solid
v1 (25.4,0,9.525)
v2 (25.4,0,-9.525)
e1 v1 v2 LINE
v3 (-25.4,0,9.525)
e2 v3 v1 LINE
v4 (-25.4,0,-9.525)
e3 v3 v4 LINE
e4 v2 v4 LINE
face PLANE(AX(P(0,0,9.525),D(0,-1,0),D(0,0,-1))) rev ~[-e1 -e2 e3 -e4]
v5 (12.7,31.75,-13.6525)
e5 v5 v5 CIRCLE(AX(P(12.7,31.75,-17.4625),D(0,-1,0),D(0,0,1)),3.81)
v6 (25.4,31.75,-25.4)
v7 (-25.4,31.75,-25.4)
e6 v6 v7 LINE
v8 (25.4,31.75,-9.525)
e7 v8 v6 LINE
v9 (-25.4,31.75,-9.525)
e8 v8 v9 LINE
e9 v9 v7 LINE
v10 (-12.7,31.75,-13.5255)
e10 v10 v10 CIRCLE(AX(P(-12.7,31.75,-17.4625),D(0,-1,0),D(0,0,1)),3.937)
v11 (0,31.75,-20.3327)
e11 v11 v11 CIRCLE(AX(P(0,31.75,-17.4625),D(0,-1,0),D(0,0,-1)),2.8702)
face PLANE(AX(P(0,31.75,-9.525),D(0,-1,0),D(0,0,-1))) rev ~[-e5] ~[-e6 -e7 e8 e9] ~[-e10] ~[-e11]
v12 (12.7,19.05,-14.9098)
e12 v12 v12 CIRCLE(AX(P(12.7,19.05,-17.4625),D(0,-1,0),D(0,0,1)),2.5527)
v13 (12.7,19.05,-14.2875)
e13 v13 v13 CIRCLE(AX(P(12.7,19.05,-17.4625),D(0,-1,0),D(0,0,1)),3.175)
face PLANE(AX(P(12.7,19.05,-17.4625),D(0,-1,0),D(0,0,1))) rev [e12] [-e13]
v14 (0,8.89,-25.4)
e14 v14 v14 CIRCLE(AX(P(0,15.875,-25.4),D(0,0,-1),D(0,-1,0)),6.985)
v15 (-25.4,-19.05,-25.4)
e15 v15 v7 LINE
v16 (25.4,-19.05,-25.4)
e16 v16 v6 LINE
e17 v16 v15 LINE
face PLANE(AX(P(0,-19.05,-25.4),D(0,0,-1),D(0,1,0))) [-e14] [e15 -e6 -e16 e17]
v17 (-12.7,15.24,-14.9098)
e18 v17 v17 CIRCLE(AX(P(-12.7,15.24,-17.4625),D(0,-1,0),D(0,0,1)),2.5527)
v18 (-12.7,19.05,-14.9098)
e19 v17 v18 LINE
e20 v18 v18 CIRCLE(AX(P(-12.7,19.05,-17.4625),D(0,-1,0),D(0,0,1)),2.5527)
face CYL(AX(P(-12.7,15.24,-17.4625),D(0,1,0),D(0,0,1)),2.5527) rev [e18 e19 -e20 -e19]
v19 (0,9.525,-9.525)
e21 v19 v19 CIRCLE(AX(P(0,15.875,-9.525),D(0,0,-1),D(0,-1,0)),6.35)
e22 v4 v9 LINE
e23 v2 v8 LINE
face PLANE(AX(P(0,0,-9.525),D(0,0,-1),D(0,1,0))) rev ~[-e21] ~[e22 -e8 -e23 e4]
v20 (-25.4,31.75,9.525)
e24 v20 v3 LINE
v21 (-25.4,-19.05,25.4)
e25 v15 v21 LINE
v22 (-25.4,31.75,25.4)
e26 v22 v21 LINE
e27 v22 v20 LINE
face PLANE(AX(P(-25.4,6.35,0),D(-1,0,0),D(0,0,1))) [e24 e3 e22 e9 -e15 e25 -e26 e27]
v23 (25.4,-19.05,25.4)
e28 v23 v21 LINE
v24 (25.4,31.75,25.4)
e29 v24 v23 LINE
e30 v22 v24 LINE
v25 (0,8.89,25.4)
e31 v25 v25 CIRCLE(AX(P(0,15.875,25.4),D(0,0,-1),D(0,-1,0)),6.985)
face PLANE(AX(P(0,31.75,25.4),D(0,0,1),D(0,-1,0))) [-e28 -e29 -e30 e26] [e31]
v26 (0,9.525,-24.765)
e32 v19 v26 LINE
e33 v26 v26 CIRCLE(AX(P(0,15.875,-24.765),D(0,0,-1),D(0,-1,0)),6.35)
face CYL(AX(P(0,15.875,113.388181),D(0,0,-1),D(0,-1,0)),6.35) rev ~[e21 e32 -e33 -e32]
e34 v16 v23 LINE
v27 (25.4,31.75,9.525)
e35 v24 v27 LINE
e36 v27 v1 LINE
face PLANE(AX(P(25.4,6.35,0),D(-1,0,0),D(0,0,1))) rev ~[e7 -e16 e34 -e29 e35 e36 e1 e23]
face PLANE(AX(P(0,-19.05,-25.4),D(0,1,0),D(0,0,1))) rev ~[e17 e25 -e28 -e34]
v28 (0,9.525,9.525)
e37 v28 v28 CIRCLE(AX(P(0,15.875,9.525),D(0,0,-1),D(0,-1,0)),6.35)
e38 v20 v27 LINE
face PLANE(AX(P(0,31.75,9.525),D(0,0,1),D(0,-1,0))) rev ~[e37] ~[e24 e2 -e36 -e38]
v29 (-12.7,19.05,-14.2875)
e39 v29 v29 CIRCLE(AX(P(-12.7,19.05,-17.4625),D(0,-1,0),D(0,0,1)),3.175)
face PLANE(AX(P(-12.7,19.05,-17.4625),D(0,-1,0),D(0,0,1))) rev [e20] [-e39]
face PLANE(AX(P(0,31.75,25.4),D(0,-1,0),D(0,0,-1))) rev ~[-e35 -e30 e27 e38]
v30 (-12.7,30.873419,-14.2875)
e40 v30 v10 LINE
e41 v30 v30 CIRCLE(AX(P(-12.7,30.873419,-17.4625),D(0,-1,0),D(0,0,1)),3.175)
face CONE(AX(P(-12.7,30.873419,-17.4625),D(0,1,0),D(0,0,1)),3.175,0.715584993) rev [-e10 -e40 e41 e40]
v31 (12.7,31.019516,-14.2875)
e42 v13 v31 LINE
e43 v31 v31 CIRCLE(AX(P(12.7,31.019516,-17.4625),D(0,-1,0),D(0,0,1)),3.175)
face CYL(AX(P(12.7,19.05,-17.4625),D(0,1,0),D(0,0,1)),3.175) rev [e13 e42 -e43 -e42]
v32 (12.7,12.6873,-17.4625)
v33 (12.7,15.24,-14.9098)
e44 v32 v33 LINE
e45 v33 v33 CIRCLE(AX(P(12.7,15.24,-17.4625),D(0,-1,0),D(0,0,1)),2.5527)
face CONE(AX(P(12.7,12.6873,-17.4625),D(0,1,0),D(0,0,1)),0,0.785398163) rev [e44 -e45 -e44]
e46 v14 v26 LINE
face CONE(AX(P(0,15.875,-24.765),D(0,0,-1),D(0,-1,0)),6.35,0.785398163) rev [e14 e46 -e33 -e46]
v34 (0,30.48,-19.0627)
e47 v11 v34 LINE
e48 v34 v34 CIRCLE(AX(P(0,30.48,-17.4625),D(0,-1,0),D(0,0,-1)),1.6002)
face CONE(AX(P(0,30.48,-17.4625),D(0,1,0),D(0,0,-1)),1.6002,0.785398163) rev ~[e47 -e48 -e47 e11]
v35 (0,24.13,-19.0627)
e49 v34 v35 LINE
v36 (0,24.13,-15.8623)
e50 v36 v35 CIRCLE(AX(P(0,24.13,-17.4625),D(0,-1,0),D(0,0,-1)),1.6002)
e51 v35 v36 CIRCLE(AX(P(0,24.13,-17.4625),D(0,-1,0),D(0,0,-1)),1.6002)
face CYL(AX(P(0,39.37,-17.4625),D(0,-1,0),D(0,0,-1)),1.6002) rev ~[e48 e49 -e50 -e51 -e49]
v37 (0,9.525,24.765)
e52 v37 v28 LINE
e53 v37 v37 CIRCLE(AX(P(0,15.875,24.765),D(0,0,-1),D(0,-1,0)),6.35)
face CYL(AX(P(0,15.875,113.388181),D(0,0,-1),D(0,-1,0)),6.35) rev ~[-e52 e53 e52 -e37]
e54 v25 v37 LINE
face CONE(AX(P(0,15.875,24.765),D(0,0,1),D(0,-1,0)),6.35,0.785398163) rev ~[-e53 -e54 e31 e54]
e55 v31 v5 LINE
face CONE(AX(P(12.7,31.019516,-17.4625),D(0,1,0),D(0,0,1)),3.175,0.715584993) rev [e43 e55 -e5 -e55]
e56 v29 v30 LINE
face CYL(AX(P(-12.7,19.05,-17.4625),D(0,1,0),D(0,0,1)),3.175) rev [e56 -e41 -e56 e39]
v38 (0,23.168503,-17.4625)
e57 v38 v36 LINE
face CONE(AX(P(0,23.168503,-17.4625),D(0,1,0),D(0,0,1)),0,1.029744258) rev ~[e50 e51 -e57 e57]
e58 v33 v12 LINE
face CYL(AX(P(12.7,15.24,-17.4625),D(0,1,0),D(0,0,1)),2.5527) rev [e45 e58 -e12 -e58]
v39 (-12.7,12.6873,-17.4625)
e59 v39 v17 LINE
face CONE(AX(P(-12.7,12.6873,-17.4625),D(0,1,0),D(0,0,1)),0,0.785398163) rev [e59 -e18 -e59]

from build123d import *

# Parameters (mm, degrees)
BASE_BLOCK_DEPTH         = 25.4
DOWEL_HOLE_0_126IN_D     = 3.2004
DOWEL_HOLE_0_126IN_DEPTH = 7.62
DOWEL_HOLE_0_126IN_TIP   = 0.961497163
DOWEL_HOLE_CHAMFER_SIZE  = 1.27
BORE_0_5IN_THRU_D        = 12.7
BORE_EDGE_CHAMFER_SIZE   = 0.635


with BuildPart() as part:
    # Base Block Profile Sketch → Base Block (new, symmetric)
    with BuildSketch(Plane(origin=(0, 0, 0), x_dir=(0, 0, -1), z_dir=(1, 0, 0))):
        Polygon((-9.525, 0), (9.525, 0), (9.525, 31.75), (25.4, 31.75), (25.4, 0), (25.4, -19.05), (-25.4, -19.05), (-25.4, 0), (-25.4, 31.75), (-9.525, 31.75), align=None)
    extrude(amount=BASE_BLOCK_DEPTH, both=True)

    # Dowel Hole 0.126in
    with Locations(Plane(origin=(0, 31.75, -17.4625), x_dir=(0, 0, 1), z_dir=(0, 1, 0))):
        with Locations((0, 0)):
            Hole(DOWEL_HOLE_0_126IN_D / 2, depth=DOWEL_HOLE_0_126IN_DEPTH)
            with Locations((0, 0, -(DOWEL_HOLE_0_126IN_DEPTH + DOWEL_HOLE_0_126IN_TIP / 2))):  # 118° drill point
                Cone(0, DOWEL_HOLE_0_126IN_D / 2, DOWEL_HOLE_0_126IN_TIP, mode=Mode.SUBTRACT)

    # Dowel Hole Chamfer
    dowel_hole_chamfer_edges = [part.edges().sort_by_distance(p)[0] for p in [
        (0, 31.75, -15.8623),
    ]]
    chamfer(dowel_hole_chamfer_edges, length=DOWEL_HOLE_CHAMFER_SIZE)

    # Sketch5 → Tapped Hole M-quarter-20 A (revolve, cut)
    with BuildSketch(Plane(origin=(12.7, 31.75, -17.4625), x_dir=(0, 0, 1), z_dir=(1, 0, 0))):
        Polygon((0, 0), (0, 19.0627), (2.5527, 16.51), (2.5527, 12.7), (3.175, 12.7), (3.175, 0.730483939), (3.81, 0), align=None)
    revolve(axis=Axis((12.7, 38.1, -17.4625), (0, -1, 0)), mode=Mode.SUBTRACT)

    # Sketch6 → Tapped Hole M-quarter-20 B (revolve, cut)
    with BuildSketch(Plane(origin=(-12.7, 31.75, -17.4625), x_dir=(0, 0, 1), z_dir=(1, 0, 0))):
        Polygon((0, 0), (0, 19.0627), (2.5527, 16.51), (2.5527, 12.7), (3.175, 12.7), (3.175, 0.876580726), (3.937, 0), align=None)
    revolve(axis=Axis((-12.7, 38.1, -17.4625), (0, -1, 0)), mode=Mode.SUBTRACT)

    # Bore 0.5in Thru (through all)
    with Locations(Plane(origin=(0, 15.875, 25.4), x_dir=(0, 1, 0), z_dir=(0, 0, 1))):
        with Locations((0, 0)):
            Hole(BORE_0_5IN_THRU_D / 2)

    # Bore Edge Chamfer
    bore_edge_chamfer_edges = [part.edges().sort_by_distance(p)[0] for p in [
        (0, 22.225, -25.4),
        (0, 22.225, 25.4),
    ]]
    chamfer(bore_edge_chamfer_edges, length=BORE_EDGE_CHAMFER_SIZE)


solid = part.part
